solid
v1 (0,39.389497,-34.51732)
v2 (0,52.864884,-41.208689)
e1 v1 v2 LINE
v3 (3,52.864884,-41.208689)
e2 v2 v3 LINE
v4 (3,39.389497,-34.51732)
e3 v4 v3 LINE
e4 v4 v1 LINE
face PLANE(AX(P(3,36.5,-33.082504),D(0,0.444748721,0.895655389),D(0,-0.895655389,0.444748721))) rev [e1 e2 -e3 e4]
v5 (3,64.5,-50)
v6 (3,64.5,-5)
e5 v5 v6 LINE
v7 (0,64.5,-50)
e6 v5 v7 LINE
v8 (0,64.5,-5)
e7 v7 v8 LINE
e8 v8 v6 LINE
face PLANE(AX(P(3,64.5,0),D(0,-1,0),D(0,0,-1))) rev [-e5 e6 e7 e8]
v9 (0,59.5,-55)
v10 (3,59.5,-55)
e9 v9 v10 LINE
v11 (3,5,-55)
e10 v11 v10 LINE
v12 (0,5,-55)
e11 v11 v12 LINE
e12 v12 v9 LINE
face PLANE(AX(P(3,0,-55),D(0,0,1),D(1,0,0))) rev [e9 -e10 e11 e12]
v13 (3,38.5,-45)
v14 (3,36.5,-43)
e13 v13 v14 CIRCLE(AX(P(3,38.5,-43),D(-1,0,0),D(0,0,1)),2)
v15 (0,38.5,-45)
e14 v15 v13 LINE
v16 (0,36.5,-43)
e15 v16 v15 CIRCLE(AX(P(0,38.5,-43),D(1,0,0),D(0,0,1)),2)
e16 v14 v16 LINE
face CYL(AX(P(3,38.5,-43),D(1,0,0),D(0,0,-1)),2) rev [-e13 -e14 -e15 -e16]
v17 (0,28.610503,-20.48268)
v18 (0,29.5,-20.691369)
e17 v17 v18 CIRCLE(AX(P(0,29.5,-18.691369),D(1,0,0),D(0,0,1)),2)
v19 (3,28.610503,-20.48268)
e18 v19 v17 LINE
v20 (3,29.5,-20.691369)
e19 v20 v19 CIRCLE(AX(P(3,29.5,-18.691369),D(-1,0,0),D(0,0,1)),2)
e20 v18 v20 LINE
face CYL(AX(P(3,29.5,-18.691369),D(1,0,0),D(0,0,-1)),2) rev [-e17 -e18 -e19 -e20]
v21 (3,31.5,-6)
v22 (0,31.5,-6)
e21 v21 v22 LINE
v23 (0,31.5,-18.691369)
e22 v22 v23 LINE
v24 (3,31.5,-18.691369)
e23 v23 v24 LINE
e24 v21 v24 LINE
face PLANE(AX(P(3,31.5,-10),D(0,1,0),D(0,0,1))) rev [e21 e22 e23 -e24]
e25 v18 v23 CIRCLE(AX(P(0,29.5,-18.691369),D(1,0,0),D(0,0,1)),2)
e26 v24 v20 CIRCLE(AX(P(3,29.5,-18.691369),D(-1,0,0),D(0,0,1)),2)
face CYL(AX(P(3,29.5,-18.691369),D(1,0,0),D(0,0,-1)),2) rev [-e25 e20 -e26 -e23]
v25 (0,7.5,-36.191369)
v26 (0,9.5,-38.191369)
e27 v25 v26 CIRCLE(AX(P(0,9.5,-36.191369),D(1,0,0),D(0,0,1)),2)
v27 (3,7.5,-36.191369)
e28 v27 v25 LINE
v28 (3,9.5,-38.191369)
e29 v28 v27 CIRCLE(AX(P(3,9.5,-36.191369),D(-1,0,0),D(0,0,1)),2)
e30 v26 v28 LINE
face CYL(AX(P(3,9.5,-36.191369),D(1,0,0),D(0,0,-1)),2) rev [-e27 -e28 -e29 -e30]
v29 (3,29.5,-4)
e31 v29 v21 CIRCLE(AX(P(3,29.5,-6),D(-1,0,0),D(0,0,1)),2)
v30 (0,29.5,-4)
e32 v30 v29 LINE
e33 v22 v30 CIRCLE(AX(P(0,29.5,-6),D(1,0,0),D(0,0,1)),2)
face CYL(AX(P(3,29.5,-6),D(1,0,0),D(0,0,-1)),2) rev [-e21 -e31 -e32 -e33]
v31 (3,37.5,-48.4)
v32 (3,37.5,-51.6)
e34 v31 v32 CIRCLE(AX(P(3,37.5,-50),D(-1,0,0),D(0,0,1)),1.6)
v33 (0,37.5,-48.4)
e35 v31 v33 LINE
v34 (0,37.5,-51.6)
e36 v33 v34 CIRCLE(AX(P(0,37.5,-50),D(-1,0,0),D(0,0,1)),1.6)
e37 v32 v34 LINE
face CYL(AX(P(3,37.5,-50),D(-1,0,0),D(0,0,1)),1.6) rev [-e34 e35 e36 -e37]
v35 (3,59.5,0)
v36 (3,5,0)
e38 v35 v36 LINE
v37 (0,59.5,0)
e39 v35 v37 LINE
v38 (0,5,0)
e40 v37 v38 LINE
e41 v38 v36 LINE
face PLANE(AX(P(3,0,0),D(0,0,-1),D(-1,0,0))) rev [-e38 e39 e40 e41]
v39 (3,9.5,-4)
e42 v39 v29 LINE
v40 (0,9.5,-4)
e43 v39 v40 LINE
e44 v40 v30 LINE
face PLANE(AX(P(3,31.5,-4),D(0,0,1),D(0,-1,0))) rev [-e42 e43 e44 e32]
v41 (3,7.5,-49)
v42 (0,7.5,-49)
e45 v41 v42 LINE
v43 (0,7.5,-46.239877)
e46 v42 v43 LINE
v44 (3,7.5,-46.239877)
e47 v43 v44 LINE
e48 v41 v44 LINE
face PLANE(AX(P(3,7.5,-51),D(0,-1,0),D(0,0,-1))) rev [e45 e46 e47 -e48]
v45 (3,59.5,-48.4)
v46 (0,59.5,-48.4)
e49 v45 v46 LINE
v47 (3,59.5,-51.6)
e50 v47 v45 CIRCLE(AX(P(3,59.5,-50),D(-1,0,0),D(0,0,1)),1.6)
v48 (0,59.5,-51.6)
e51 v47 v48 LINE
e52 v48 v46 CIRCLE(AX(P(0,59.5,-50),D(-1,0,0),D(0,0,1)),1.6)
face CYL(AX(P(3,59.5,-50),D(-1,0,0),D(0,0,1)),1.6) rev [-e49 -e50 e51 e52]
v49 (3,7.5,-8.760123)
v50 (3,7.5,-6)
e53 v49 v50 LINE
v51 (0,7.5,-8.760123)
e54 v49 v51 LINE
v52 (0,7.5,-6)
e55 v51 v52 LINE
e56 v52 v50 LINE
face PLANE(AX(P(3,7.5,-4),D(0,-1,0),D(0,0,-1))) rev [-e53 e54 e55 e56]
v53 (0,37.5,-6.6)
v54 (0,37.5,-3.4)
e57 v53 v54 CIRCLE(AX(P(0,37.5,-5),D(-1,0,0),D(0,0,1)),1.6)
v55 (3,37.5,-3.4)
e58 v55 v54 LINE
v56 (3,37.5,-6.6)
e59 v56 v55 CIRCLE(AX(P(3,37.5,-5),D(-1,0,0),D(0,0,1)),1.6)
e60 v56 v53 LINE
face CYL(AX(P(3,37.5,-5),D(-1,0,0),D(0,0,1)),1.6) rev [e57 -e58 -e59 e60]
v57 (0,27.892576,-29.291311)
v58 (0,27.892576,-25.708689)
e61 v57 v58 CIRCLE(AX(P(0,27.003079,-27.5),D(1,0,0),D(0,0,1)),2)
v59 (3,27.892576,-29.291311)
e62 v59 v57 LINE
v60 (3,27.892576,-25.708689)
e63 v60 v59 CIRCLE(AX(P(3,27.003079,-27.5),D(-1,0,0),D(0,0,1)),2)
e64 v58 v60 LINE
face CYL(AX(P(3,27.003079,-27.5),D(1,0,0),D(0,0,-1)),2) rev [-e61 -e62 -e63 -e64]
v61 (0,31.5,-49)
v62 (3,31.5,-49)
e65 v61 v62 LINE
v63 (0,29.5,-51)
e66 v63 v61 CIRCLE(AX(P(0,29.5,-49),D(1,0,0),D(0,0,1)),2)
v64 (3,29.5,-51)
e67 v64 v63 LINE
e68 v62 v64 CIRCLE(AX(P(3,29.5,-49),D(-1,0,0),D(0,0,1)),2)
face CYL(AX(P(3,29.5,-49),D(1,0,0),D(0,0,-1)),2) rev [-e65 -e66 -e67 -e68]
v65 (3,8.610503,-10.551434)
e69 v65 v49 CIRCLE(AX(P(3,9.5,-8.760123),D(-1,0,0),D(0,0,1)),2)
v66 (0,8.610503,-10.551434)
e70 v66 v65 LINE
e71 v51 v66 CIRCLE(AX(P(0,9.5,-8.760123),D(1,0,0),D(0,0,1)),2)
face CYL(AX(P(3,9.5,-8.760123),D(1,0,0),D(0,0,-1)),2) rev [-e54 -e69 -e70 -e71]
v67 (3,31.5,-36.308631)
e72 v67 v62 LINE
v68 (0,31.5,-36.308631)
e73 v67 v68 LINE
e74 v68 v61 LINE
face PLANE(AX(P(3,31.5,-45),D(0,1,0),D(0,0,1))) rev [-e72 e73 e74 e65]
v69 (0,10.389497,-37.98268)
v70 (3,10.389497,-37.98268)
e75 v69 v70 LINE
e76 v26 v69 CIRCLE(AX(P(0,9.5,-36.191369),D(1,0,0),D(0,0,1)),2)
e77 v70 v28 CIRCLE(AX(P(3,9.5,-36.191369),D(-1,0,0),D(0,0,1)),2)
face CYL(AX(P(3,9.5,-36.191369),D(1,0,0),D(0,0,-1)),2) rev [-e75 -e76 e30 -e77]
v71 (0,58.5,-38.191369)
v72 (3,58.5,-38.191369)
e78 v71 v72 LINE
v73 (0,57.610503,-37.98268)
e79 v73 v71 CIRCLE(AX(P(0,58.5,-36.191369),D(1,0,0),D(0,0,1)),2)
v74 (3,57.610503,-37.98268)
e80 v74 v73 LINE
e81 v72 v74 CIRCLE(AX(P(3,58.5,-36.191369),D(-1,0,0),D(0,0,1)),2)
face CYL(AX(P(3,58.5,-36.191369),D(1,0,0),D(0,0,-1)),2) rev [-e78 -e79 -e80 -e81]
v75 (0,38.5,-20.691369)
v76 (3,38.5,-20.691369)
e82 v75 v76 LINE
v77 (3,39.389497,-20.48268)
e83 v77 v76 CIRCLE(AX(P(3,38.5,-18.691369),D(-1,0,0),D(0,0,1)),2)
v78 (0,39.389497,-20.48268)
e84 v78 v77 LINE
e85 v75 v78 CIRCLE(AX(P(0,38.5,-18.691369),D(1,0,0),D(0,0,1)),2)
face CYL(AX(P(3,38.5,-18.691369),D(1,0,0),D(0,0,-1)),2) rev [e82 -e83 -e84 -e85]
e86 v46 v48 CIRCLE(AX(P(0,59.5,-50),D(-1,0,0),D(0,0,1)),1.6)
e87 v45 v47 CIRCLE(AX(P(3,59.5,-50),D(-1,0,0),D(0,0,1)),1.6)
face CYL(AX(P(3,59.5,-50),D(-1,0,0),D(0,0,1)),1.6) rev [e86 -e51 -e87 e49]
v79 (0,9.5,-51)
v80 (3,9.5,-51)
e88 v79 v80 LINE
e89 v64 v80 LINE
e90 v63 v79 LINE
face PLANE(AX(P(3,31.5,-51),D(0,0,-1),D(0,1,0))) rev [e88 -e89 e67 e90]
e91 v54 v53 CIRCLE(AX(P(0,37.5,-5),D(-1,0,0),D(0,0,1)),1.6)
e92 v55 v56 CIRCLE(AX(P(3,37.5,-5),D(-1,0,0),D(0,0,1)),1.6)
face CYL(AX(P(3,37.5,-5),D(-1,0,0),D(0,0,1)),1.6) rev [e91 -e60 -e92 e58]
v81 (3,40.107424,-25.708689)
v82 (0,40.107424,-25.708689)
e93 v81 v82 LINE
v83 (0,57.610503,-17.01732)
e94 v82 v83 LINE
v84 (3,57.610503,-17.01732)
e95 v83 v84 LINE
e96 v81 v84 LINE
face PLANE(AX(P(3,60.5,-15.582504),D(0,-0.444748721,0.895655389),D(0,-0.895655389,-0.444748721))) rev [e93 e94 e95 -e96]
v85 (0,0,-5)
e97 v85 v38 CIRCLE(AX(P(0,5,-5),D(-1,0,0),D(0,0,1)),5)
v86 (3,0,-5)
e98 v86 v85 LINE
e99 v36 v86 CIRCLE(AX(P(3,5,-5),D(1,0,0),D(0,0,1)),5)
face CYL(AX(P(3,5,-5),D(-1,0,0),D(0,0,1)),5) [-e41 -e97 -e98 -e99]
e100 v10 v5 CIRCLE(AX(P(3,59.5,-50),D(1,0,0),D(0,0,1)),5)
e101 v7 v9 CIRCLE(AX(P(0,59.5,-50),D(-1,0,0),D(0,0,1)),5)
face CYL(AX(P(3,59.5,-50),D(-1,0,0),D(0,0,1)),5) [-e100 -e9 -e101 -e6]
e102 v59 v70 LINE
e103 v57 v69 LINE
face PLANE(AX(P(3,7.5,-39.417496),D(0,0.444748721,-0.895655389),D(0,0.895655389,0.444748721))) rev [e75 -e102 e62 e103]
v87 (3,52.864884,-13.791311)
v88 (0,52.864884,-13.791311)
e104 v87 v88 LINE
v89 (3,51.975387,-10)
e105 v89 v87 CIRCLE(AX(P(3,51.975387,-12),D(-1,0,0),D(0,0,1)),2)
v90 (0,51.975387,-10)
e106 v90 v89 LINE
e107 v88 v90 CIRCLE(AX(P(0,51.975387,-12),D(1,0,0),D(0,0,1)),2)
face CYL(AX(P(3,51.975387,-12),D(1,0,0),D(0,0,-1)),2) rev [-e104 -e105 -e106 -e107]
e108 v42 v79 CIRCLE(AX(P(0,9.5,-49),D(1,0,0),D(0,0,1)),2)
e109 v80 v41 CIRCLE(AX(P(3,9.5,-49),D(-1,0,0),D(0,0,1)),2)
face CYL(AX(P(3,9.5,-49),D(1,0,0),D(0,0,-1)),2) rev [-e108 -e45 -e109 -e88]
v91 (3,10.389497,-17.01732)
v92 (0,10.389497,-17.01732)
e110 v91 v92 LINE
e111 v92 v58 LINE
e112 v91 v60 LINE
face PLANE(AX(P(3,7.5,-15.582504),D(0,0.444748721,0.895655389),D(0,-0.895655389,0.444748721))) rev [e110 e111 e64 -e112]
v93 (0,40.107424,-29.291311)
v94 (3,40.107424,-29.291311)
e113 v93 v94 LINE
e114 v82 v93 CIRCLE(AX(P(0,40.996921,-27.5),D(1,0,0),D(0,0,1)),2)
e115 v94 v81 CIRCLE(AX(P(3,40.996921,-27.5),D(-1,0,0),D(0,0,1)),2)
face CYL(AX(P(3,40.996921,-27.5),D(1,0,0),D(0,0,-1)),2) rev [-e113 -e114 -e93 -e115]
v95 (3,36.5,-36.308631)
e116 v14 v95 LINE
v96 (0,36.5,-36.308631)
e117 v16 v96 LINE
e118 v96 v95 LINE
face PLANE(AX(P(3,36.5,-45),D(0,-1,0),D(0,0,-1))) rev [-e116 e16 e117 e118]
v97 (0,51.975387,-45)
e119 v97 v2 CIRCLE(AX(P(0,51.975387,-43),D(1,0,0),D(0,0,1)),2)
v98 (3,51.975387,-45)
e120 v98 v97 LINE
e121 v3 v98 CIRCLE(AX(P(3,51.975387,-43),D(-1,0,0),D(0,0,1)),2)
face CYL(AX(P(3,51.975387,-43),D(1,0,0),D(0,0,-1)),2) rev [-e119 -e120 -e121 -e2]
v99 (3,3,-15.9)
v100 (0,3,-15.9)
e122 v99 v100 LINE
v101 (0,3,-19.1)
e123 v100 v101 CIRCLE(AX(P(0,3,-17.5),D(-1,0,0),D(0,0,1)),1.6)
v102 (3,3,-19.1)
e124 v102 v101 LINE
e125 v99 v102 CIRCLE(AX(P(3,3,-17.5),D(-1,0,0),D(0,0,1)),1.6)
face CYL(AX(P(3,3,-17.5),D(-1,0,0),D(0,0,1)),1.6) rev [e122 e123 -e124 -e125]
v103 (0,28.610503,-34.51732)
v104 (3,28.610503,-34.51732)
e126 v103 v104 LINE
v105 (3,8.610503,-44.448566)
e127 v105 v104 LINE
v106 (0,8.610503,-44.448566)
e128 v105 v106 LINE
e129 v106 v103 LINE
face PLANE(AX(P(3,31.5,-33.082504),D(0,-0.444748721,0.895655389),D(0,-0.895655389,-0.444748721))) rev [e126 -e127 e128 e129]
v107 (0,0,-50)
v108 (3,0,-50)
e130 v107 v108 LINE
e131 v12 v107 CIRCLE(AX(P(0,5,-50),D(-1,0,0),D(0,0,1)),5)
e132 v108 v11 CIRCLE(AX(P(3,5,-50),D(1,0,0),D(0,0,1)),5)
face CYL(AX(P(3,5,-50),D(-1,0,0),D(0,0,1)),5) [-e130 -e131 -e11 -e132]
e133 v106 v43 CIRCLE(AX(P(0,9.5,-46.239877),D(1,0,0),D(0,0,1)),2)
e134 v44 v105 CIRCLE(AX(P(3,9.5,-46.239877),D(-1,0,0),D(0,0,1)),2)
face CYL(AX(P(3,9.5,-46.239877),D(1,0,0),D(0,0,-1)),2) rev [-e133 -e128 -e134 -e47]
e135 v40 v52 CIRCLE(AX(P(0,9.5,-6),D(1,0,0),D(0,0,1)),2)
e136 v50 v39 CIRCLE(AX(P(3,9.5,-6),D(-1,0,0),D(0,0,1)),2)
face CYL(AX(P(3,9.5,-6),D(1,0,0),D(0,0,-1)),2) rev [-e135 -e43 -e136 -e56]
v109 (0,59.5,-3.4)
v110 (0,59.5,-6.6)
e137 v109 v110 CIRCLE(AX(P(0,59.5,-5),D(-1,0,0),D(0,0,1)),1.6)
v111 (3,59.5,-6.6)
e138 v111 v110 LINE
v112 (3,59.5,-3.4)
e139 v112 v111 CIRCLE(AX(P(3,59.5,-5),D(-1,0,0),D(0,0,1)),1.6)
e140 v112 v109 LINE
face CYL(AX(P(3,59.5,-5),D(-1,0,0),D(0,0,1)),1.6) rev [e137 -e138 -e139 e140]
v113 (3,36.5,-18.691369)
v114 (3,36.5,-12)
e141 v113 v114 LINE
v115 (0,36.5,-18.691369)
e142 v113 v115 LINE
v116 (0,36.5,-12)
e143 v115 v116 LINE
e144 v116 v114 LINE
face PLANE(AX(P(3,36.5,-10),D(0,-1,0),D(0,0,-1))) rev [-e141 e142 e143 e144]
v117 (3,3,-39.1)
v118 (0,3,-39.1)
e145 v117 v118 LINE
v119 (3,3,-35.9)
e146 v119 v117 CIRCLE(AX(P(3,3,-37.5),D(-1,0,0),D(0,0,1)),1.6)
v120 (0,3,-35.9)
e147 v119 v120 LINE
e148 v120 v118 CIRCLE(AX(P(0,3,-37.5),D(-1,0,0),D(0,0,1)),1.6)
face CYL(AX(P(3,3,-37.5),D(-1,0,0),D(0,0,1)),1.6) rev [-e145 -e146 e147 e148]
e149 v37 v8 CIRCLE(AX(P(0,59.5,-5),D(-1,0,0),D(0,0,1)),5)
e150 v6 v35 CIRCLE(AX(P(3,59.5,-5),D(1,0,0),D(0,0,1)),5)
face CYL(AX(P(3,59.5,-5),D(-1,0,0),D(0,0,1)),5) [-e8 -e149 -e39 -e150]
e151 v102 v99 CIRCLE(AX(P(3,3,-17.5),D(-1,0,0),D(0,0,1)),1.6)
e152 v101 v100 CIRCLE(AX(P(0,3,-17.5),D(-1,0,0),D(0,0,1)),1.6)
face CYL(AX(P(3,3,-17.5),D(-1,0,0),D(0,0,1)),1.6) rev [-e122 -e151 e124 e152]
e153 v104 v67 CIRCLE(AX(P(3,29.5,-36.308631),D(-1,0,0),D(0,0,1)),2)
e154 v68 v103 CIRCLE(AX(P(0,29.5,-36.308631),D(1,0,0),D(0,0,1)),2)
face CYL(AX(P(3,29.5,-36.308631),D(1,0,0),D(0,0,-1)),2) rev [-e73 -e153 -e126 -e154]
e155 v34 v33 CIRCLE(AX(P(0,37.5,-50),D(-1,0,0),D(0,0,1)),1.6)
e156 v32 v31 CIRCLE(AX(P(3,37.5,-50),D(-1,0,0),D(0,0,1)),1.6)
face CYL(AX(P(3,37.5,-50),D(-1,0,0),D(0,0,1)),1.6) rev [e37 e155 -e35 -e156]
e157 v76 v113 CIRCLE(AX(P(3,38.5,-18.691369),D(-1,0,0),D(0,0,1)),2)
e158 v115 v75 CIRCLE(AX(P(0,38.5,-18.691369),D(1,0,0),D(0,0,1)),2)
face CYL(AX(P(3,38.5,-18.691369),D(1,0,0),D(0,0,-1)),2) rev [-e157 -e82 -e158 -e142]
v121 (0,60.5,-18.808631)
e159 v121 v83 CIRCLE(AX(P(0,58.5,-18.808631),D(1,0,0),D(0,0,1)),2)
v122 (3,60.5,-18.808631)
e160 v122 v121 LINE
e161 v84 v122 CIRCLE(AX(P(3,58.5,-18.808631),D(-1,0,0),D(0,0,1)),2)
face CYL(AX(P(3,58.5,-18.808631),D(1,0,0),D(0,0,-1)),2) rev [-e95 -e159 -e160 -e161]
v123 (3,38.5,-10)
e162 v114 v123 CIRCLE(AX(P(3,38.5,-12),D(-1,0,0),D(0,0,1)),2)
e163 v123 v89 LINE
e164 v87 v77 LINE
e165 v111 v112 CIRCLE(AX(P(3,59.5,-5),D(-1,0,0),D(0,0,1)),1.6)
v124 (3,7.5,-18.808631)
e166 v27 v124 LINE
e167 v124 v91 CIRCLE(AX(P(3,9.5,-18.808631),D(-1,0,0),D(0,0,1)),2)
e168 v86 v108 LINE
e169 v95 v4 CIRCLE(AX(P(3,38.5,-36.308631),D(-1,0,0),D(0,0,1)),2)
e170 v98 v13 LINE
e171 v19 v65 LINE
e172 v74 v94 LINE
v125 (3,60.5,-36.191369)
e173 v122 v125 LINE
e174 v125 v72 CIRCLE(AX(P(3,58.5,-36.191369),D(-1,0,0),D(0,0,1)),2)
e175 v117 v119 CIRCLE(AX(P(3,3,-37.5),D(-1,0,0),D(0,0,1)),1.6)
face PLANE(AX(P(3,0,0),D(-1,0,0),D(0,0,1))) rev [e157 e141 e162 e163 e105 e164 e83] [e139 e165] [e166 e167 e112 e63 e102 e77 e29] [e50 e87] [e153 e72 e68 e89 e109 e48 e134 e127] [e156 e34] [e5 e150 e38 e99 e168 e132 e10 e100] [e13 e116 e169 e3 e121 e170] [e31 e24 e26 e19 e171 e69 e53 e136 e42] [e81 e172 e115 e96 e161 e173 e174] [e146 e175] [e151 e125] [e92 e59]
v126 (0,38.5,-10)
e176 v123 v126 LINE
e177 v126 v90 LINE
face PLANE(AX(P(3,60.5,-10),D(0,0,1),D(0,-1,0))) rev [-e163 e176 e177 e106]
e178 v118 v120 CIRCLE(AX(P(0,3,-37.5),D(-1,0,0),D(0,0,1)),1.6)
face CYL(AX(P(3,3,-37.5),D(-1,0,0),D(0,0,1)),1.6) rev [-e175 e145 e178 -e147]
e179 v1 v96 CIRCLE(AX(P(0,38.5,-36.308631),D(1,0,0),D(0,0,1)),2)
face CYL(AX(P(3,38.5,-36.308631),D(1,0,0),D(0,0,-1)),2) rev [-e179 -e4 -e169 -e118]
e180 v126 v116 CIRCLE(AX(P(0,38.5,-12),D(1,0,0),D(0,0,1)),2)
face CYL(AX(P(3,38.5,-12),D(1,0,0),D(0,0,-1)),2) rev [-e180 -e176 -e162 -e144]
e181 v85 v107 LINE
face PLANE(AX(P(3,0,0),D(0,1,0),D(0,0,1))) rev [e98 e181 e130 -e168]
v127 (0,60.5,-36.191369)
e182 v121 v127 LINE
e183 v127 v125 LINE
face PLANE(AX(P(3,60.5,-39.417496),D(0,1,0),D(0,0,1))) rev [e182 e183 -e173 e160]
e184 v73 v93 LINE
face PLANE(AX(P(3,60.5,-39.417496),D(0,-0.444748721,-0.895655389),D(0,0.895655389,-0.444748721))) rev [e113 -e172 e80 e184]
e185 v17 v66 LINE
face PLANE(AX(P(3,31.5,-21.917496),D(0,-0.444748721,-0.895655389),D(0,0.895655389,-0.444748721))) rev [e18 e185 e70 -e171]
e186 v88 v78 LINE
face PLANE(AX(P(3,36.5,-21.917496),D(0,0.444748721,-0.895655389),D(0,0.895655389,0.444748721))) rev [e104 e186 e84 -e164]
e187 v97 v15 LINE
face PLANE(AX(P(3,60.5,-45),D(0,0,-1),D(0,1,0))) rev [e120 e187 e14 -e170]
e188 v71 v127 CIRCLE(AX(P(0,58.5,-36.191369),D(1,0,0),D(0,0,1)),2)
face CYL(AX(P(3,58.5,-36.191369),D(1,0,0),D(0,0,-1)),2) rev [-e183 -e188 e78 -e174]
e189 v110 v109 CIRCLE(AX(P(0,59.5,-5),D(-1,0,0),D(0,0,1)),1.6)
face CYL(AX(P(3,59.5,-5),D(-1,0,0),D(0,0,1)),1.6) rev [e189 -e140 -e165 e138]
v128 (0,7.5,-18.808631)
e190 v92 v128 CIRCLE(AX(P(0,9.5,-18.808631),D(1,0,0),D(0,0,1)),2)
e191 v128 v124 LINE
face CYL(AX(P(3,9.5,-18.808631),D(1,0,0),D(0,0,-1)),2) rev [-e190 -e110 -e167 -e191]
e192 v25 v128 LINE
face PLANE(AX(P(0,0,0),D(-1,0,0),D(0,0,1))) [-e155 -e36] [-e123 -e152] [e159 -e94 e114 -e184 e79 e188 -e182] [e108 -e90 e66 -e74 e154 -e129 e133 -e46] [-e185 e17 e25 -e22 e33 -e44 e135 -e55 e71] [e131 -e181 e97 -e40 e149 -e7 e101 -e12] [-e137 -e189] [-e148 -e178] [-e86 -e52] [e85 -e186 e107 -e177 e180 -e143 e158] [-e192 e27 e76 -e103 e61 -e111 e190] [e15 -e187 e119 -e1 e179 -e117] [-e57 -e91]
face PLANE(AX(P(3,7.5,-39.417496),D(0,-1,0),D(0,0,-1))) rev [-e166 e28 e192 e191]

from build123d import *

# Parameters (mm, degrees)
SKETCH_2_W          = 55
SKETCH_2_H          = 64.5
EXTRUDE_1_DEPTH     = 3
SKETCH_3_R          = 1.6
CUT_EXTRUDE_1_DEPTH = 3
FILLET_1_R          = 5
CUT_EXTRUDE_2_DEPTH = 3
FILLET_2_R          = 2


with BuildPart() as part:
    # 草图2 → 凸台-拉伸1 (new body)
    with BuildSketch(Plane(origin=(0, 0, 0), x_dir=(0, 0, -1), z_dir=(1, 0, 0))):
        with Locations((27.5, 32.25)):
            Rectangle(SKETCH_2_W, SKETCH_2_H)
    extrude(amount=EXTRUDE_1_DEPTH)

    # 草图3 → 切除-拉伸1 (cut)
    with BuildSketch(Plane.ZY):
        with Locations((-5, 59.5)):
            Circle(SKETCH_3_R)
        with Locations((-5, 37.5)):
            Circle(SKETCH_3_R)
        with Locations((-50, 59.5)):
            Circle(SKETCH_3_R)
        with Locations((-50, 37.5)):
            Circle(SKETCH_3_R)
        with Locations((-37.5, 3)):
            Circle(SKETCH_3_R)
        with Locations((-17.5, 3)):
            Circle(SKETCH_3_R)
    extrude(amount=-CUT_EXTRUDE_1_DEPTH, mode=Mode.SUBTRACT)

    # 圆角1
    fillet_1_edges = [part.edges().sort_by_distance(p)[0] for p in [
        (1.5, 64.5, 0),
        (1.5, 64.5, -55),
        (1.5, 0, -55),
        (1.5, 0, 0),
    ]]
    fillet(fillet_1_edges, radius=FILLET_1_R)

    # 草图4 → 切除-拉伸2 (cut)
    with BuildSketch(Plane.ZY):
        Polygon((-39.417495765, 60.5), (-27.5, 36.5), (-15.582504235, 60.5), align=None)
        Polygon((-45, 60.5), (-45, 36.5), (-33.082504235, 36.5), align=None)
        Polygon((-21.917495765, 36.5), (-10, 60.5), (-10, 36.5), align=None)
        Polygon((-10, 31.5), (-21.917495765, 31.5), (-10, 7.5), (-4, 7.5), (-4, 31.5), align=None)
        Polygon((-39.417495765, 7.5), (-27.5, 31.5), (-15.582504235, 7.5), align=None)
        Polygon((-45, 31.5), (-33.082504235, 31.5), (-45, 7.5), (-51, 7.5), (-51, 31.5), align=None)
    extrude(amount=-CUT_EXTRUDE_2_DEPTH, mode=Mode.SUBTRACT)

    # 圆角2
    fillet_2_edges = [part.edges().sort_by_distance(p)[0] for p in [
        (1.5, 60.5, -45),
        (1.5, 36.5, -33.082504235),
        (1.5, 36.5, -45),
        (1.5, 60.5, -39.417495765),
        (1.5, 60.5, -15.582504235),
        (1.5, 36.5, -27.5),
        (1.5, 31.5, -27.5),
        (1.5, 7.5, -15.582504235),
        (1.5, 7.5, -39.417495765),
        (1.5, 31.5, -4),
        (1.5, 7.5, -4),
        (1.5, 7.5, -10),
        (1.5, 31.5, -21.917495765),
        (1.5, 7.5, -51),
        (1.5, 31.5, -51),
        (1.5, 31.5, -33.082504235),
        (1.5, 7.5, -45),
        (1.5, 36.5, -10),
        (1.5, 36.5, -21.917495765),
        (1.5, 60.5, -10),
    ]]
    fillet(fillet_2_edges, radius=FILLET_2_R)


solid = part.part
